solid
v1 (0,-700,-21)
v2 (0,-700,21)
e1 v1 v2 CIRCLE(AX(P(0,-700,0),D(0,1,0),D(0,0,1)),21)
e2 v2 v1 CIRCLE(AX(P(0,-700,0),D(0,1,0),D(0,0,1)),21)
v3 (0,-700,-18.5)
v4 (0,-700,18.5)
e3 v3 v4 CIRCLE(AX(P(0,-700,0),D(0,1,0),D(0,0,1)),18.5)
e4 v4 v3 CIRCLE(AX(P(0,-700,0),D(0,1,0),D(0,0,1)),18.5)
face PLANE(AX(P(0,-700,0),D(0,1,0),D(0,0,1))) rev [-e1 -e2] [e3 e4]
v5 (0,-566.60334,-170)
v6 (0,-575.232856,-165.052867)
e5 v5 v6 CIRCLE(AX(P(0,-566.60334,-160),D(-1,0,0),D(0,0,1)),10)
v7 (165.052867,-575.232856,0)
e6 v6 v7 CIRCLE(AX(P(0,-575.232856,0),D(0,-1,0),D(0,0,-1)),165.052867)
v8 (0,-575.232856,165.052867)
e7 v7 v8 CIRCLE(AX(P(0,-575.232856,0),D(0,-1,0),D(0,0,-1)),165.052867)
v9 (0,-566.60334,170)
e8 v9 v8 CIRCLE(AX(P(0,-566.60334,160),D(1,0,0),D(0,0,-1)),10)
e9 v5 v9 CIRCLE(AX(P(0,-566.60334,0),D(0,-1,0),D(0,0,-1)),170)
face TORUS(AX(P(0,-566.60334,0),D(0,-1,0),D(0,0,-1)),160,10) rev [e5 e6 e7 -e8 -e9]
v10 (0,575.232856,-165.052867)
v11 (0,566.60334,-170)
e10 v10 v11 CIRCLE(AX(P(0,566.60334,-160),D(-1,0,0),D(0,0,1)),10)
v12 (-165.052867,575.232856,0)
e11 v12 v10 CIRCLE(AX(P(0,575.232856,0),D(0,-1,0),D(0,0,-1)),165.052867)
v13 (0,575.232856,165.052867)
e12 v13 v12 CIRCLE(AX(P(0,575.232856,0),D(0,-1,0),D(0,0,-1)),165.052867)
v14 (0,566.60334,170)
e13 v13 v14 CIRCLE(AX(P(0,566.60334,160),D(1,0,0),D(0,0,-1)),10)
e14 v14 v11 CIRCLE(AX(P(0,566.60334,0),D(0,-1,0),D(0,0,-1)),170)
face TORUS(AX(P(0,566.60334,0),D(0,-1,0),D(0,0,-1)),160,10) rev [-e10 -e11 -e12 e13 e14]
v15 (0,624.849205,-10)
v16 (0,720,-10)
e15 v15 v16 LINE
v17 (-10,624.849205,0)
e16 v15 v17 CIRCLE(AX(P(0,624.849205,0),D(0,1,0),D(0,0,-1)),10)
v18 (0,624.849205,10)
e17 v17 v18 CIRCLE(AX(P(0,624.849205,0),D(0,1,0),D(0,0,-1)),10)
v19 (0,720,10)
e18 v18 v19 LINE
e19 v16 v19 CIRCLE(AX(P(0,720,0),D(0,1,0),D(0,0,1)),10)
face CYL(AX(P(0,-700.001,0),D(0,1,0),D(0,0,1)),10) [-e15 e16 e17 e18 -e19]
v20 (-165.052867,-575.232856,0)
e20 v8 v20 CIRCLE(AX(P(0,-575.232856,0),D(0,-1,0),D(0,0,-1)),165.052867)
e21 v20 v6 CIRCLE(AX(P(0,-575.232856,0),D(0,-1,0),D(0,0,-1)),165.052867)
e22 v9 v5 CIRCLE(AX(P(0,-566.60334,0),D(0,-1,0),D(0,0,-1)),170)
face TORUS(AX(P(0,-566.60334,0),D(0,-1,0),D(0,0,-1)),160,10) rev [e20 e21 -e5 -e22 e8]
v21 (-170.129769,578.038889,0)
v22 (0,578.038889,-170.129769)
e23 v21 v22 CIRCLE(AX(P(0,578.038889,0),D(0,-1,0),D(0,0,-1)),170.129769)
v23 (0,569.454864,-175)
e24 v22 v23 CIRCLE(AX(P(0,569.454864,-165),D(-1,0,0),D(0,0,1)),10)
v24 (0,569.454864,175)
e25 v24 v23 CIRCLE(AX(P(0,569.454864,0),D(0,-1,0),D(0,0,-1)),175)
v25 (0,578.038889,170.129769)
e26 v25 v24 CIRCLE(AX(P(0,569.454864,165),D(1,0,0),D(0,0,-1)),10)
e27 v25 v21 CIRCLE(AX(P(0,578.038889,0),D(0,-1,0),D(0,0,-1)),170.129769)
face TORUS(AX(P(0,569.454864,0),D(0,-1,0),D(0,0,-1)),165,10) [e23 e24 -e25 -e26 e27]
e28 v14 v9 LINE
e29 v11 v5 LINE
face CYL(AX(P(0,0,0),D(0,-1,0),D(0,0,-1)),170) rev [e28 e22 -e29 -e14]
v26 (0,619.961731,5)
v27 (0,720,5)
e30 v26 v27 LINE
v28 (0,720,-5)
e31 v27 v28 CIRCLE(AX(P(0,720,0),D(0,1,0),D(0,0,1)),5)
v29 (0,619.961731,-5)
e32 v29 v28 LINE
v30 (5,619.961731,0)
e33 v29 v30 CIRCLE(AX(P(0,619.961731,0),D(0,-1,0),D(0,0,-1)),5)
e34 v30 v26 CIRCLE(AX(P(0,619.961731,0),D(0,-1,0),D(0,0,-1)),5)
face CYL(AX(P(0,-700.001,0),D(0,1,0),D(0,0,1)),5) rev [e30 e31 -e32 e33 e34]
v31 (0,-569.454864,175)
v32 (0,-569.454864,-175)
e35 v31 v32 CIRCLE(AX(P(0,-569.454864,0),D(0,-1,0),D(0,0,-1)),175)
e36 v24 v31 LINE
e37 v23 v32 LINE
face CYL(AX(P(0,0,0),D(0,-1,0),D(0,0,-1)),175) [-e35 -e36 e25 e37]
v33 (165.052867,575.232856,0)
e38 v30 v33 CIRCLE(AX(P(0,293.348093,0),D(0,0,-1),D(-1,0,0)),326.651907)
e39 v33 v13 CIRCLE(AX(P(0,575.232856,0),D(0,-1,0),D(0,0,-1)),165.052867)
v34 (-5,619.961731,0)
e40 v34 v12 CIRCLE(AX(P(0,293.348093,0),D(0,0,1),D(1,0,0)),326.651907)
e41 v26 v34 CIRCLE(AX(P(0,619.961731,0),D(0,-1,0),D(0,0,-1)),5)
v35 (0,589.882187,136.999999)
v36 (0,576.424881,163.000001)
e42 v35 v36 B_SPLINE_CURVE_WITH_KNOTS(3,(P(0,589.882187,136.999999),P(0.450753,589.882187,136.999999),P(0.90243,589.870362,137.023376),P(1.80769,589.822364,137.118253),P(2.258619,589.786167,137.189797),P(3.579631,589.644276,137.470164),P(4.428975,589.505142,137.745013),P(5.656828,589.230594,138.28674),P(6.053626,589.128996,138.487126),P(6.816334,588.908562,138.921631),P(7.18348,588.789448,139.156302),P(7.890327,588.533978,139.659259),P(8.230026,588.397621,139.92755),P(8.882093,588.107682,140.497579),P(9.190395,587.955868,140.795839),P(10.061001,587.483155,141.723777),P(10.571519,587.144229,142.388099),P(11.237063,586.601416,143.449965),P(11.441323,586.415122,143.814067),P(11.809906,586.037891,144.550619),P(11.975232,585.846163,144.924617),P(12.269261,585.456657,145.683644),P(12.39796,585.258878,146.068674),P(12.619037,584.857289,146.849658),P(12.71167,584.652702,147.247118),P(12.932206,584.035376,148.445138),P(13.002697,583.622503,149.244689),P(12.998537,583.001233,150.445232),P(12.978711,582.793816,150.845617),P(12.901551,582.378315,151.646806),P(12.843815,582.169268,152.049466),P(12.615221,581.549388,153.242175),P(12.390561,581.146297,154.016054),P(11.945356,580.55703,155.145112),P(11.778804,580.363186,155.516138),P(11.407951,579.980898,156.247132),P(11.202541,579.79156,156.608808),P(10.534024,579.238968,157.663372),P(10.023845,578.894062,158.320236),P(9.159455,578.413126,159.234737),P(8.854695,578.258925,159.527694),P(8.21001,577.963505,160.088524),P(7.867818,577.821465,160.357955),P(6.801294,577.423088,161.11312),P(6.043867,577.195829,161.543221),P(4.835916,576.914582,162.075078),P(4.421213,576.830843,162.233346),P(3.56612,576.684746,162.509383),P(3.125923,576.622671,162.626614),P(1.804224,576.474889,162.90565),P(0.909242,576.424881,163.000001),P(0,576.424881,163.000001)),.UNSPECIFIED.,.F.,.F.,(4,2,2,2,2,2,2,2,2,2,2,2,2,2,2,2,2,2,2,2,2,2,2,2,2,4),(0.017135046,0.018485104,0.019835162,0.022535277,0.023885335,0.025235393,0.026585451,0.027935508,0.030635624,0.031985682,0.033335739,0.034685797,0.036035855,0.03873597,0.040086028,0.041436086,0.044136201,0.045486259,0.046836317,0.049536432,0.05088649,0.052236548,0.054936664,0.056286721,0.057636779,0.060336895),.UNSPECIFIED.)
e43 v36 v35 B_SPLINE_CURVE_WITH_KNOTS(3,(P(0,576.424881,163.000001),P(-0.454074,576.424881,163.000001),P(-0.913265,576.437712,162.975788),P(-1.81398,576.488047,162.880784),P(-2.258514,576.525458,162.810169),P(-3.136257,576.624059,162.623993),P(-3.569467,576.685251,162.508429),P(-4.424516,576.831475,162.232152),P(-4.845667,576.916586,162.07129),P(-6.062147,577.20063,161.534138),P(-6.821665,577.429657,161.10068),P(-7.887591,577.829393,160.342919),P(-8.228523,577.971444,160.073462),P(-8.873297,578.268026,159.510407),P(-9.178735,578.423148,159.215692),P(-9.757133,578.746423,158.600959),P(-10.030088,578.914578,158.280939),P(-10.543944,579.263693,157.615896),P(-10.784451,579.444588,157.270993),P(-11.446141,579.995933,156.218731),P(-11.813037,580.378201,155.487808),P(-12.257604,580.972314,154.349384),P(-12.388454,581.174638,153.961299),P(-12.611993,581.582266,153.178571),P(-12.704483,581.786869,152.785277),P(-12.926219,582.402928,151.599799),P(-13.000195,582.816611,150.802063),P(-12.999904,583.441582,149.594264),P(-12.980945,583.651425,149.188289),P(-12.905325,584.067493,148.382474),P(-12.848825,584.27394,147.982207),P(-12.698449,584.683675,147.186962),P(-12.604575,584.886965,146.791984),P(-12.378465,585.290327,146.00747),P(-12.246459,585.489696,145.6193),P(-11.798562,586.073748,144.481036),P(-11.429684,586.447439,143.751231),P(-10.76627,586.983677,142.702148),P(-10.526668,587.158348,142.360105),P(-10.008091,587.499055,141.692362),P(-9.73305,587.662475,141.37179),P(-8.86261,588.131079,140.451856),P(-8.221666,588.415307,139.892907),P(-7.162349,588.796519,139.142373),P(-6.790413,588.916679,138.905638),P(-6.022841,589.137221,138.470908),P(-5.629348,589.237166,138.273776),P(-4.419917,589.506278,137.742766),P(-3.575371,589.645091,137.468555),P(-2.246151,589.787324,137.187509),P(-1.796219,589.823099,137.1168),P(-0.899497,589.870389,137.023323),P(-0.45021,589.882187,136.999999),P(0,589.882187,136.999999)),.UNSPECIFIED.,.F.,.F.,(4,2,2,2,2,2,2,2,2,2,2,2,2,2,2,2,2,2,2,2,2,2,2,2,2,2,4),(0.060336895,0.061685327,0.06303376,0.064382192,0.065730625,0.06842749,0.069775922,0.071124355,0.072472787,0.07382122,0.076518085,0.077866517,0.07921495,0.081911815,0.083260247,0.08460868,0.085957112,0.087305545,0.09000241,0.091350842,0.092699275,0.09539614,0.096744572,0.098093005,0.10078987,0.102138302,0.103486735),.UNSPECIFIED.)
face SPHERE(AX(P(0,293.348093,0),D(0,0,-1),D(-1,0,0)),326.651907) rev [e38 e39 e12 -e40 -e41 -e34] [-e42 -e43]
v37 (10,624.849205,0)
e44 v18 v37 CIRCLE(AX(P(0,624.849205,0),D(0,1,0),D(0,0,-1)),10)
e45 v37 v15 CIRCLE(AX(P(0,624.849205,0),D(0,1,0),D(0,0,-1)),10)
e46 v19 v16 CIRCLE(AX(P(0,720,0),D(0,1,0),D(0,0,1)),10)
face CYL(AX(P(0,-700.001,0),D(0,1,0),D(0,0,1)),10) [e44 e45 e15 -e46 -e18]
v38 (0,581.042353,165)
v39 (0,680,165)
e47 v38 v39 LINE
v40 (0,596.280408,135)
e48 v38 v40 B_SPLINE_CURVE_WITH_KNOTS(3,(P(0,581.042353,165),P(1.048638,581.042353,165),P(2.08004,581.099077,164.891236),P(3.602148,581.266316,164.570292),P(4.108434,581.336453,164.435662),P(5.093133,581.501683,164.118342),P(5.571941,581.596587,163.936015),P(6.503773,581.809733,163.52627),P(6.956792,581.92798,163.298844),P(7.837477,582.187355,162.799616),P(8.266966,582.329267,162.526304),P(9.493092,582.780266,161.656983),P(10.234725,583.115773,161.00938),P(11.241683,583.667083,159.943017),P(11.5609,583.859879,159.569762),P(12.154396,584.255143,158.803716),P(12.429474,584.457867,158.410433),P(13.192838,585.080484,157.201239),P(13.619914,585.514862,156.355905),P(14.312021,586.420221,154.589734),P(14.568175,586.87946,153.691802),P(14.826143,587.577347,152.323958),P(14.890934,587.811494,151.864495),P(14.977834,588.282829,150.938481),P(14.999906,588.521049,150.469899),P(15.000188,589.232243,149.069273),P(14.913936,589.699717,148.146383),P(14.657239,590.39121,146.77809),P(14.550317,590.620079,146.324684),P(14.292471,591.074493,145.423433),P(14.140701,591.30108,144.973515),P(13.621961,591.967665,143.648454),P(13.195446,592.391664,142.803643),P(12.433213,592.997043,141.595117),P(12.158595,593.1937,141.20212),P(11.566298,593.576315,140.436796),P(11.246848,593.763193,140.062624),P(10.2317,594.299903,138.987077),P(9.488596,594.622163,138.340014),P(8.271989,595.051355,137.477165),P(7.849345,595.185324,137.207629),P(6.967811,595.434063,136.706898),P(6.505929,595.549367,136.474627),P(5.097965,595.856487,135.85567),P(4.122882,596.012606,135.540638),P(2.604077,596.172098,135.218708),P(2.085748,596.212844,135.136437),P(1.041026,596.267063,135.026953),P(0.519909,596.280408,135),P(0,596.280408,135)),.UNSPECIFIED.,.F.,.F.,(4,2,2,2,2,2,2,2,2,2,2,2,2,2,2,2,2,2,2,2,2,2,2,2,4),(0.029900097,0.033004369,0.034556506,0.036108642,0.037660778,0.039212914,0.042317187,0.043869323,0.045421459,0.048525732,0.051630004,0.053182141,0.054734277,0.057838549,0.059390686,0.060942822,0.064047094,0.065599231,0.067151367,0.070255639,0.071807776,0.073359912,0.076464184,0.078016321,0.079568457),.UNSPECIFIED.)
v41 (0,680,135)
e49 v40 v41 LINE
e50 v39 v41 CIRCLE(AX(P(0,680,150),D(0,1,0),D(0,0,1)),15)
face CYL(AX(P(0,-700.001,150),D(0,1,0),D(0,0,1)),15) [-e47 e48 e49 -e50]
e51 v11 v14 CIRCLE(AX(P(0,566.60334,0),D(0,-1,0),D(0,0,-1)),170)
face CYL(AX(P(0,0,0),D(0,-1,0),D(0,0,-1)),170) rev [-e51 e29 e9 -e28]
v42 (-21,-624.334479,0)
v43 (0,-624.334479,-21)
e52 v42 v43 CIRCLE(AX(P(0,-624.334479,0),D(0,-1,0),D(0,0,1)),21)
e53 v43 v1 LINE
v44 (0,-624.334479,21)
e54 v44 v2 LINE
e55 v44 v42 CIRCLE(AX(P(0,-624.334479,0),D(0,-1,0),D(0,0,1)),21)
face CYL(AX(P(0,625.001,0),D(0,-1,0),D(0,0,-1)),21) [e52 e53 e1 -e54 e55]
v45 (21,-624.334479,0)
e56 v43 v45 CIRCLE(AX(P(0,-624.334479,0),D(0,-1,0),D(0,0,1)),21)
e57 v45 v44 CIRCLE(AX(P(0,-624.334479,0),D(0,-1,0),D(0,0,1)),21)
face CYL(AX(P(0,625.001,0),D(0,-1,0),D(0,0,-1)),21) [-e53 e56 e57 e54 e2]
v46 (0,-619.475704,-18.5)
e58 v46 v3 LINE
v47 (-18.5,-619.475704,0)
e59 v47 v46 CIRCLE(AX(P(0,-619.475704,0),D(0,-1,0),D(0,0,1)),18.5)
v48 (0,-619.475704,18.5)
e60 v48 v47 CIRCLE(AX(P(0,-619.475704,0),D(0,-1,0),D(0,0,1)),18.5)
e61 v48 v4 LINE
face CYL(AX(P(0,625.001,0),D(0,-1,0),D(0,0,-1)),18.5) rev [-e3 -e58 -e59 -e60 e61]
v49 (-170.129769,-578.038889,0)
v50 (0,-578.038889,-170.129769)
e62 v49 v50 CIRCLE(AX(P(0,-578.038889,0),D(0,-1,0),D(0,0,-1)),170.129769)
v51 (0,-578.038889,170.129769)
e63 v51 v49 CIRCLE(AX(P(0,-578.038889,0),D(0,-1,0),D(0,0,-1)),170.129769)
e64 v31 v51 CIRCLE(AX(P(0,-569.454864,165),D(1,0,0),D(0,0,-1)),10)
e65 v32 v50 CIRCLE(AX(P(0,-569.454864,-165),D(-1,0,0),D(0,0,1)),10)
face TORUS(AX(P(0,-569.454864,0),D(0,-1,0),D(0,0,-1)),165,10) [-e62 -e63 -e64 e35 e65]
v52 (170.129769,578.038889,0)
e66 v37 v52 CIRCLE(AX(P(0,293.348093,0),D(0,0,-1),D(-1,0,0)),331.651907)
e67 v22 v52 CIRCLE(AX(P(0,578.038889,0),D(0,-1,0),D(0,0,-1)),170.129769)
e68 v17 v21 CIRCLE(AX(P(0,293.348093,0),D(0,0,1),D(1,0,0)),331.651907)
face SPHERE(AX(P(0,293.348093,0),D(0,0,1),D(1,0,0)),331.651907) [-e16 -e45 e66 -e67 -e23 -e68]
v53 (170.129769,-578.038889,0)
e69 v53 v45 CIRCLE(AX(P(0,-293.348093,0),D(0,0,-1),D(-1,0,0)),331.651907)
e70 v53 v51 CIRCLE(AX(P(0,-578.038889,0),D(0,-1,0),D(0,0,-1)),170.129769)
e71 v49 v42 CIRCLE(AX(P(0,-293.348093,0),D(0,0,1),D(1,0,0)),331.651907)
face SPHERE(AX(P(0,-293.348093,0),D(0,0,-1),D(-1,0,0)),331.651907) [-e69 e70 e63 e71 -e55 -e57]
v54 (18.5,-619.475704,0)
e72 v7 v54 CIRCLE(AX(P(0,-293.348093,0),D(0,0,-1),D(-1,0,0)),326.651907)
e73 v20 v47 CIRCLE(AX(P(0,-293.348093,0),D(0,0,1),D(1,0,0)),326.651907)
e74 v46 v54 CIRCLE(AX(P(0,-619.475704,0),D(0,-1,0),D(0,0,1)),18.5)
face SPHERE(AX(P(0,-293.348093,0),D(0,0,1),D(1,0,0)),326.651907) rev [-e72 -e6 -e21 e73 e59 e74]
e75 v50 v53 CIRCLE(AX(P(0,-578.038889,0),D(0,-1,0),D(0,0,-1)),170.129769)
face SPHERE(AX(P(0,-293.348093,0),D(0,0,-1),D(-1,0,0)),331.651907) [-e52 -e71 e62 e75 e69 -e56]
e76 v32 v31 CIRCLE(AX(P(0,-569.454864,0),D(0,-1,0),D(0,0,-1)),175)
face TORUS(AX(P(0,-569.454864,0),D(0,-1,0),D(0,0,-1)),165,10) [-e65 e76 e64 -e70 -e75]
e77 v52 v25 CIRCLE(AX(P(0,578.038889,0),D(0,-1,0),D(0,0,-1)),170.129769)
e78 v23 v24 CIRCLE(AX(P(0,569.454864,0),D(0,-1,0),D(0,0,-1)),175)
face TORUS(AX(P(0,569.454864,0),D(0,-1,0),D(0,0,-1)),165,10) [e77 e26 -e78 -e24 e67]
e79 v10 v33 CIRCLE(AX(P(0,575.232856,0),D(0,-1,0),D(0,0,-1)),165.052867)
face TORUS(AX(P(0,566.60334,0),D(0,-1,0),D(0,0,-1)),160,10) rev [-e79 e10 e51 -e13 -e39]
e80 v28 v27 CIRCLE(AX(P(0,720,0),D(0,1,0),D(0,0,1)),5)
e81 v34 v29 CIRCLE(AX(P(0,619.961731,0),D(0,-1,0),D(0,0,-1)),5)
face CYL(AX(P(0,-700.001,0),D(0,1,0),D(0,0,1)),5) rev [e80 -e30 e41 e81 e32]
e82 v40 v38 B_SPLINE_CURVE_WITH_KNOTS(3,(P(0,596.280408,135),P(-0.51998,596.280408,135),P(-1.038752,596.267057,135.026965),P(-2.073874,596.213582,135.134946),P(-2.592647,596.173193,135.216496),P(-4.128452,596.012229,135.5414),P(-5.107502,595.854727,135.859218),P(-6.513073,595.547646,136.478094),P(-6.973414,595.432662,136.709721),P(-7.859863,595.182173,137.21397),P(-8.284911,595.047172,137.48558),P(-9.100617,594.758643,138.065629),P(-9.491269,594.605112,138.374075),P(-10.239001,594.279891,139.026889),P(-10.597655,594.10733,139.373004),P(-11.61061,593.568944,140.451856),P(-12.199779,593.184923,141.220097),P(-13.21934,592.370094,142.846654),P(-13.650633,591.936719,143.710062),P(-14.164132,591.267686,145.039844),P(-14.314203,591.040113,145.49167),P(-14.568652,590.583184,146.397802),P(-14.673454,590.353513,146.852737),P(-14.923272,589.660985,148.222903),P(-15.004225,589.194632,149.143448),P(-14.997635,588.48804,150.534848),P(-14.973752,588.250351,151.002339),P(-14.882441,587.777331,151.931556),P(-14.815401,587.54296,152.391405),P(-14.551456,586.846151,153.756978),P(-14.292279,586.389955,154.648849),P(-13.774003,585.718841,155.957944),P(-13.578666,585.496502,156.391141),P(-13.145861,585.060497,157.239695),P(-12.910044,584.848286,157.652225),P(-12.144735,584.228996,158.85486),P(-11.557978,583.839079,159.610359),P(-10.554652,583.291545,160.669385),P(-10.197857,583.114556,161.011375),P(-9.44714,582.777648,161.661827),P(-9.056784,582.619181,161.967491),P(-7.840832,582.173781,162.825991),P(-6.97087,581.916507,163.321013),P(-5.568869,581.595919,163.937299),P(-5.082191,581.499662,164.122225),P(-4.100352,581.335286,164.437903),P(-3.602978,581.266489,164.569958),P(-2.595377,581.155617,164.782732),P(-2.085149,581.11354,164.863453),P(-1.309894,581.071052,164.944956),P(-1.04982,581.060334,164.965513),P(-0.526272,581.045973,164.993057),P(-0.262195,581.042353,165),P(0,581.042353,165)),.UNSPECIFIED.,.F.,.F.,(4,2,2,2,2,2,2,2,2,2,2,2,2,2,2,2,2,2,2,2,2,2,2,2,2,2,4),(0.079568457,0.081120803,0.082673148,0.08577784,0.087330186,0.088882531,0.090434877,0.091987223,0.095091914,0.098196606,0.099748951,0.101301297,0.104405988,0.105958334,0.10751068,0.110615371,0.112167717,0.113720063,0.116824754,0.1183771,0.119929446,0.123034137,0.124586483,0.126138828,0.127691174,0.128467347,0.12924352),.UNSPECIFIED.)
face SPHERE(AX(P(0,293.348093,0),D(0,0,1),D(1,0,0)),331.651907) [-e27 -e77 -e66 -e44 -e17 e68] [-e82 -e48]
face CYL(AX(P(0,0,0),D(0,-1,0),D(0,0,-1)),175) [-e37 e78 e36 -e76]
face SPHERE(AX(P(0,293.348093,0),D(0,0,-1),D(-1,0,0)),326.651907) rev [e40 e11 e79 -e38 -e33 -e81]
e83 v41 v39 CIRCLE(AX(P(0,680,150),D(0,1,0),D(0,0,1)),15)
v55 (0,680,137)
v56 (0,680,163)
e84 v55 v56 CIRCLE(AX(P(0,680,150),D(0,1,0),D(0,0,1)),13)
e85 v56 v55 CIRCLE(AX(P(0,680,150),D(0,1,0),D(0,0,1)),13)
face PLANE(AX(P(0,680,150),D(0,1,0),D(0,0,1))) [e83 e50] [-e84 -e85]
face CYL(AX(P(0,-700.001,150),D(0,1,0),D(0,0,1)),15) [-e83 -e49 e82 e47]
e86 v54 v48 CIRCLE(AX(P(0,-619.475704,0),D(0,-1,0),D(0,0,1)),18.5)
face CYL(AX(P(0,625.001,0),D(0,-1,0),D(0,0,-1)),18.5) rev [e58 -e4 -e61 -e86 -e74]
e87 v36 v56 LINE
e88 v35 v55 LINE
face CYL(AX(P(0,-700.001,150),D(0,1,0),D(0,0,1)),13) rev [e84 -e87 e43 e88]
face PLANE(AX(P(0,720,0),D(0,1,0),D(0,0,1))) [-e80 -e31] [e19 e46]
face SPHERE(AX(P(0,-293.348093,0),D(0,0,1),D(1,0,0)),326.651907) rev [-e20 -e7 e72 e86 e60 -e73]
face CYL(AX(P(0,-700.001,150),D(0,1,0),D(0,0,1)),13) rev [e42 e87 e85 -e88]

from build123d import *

# Parameters (mm, degrees)
BOSS_EXTRUDE1_REACH      = 1349.915
BOSS_EXTRUDE1_END_RADIUS = 331.651906797
SKETCH2_R                = 21
SKETCH2_R_2              = 18.5
SKETCH3_R                = 18.5
CUT_EXTRUDE1_DEPTH       = 526
BOSS_EXTRUDE3_REACH      = 1443.406
BOSS_EXTRUDE3_END_RADIUS = 331.651906797
SKETCH5_R                = 10
SKETCH5_R_2              = 5
SKETCH6_R                = 5
CUT_EXTRUDE2_DEPTH       = 190
BOSS_EXTRUDE5_REACH      = 1404.016
BOSS_EXTRUDE5_END_RADIUS = 331.651906797
SKETCH8_R                = 15
SKETCH8_R_2              = 13
SKETCH9_R                = 13.000001432
CUT_EXTRUDE3_DEPTH       = 107


with BuildPart() as part:
    # Sketch1 → Revolve1 (revolve)
    with BuildSketch(Plane.XY, mode=Mode.PRIVATE) as revolve1_sk:
        with BuildLine():
            Line((175, -569.454864482), (175, 569.454864482))
            ThreePointArc((175, 569.454864482), (173.697634466, 574.389553398), (170.129769061, 578.03888856))
            ThreePointArc((170.129769061, 578.03888856), (88.246082503, 613.044224248), (0, 625))
            Line((0, 625), (0, 620))
            ThreePointArc((0, 620), (85.508108026, 608.609622217), (165.052867094, 575.232855612))
            ThreePointArc((165.052867094, 575.232855612), (168.67550203, 571.57683653), (170, 566.603340322))
            Line((170, 566.603340322), (170, -566.603340322))
            ThreePointArc((170, -566.603340322), (168.67550203, -571.57683653), (165.052867094, -575.232855612))
            ThreePointArc((165.052867094, -575.232855612), (85.508108026, -608.609622217), (0, -620))
            Line((0, -620), (0, -625))
            ThreePointArc((0, -625), (88.246082503, -613.044224248), (170.129769061, -578.03888856))
            ThreePointArc((170.129769061, -578.03888856), (173.697634466, -574.389553398), (175, -569.454864482))
        make_face()
    revolve(revolve1_sk.sketch.rotate(Axis((0, 0, 0), (0, 1, 0)), 90), axis=Axis((0, 0, 0), (0, 1, 0)))

    # Boss-Extrude1: up to this sphere (the profile starts outside it)
    boss_extrude1_end = Location((0, -293.348093203, 0)) * Sphere(BOSS_EXTRUDE1_END_RADIUS, mode=Mode.PRIVATE)
    # Sketch2 → Boss-Extrude1 (add, up to the surface)
    with BuildSketch(Plane(origin=(0, -700, 0), x_dir=(1, 0, 0), z_dir=(0, 1, 0)), mode=Mode.PRIVATE) as boss_extrude1_sk1:
        with Locations(Location((0, 0, 0), (0, 0, 180))):
            Circle(SKETCH2_R)
        with Locations(Location((0, 0, 0), (0, 0, 270))):
            Circle(SKETCH2_R_2, mode=Mode.SUBTRACT)
    boss_extrude1_tool1 = extrude(boss_extrude1_sk1.sketch, amount=BOSS_EXTRUDE1_REACH, mode=Mode.PRIVATE) - boss_extrude1_end
    add(boss_extrude1_tool1.solids().sort_by_distance((20.40603, -700, 0))[0])

    # Sketch3 → Cut-Extrude1 (cut)
    with BuildSketch(Plane(origin=(0, -700, 0), x_dir=(1, 0, 0), z_dir=(0, 1, 0))):
        Circle(SKETCH3_R)
    extrude(amount=CUT_EXTRUDE1_DEPTH, mode=Mode.SUBTRACT)

    # Boss-Extrude3: up to this sphere (the profile starts outside it)
    boss_extrude3_end = Location((0, 293.348093203, 0)) * Sphere(BOSS_EXTRUDE3_END_RADIUS, mode=Mode.PRIVATE)
    # Sketch5 → Boss-Extrude3 (add, up to the surface)
    with BuildSketch(Plane(origin=(0, 720, 0), x_dir=(1, 0, 0), z_dir=(0, 1, 0)), mode=Mode.PRIVATE) as boss_extrude3_sk1:
        with Locations(Location((0, 0, 0), (0, 0, 270))):
            Circle(SKETCH5_R)
        with Locations(Location((0, 0, 0), (0, 0, 270))):
            Circle(SKETCH5_R_2, mode=Mode.SUBTRACT)
    boss_extrude3_tool1 = extrude(boss_extrude3_sk1.sketch, amount=-BOSS_EXTRUDE3_REACH, mode=Mode.PRIVATE) - boss_extrude3_end
    add(boss_extrude3_tool1.solids().sort_by_distance((0, 720, -9.717157))[0])

    # Sketch6 → Cut-Extrude2 (cut)
    with BuildSketch(Plane(origin=(0, 720, 0), x_dir=(1, 0, 0), z_dir=(0, 1, 0))):
        with Locations(Location((0, 0, 0), (0, 0, 270))):
            Circle(SKETCH6_R)
    extrude(amount=-CUT_EXTRUDE2_DEPTH, mode=Mode.SUBTRACT)

    # Boss-Extrude5: up to this sphere (the profile starts outside it)
    boss_extrude5_end = Location((0, 293.348093203, 0)) * Sphere(BOSS_EXTRUDE5_END_RADIUS, mode=Mode.PRIVATE)
    # Sketch8 → Boss-Extrude5 (add, up to the surface)
    with BuildSketch(Plane(origin=(0, 680, 0), x_dir=(1, 0, 0), z_dir=(0, 1, 0)), mode=Mode.PRIVATE) as boss_extrude5_sk1:
        with Locations(Location((0, -150, 0), (0, 0, 270.000000007))):
            Circle(SKETCH8_R)
        with Locations(Location((0, -150, 0), (0, 0, 270))):
            Circle(SKETCH8_R_2, mode=Mode.SUBTRACT)
    boss_extrude5_tool1 = extrude(boss_extrude5_sk1.sketch, amount=-BOSS_EXTRUDE5_REACH, mode=Mode.PRIVATE) - boss_extrude5_end
    add(boss_extrude5_tool1.solids().sort_by_distance((0, 680, 135.424264))[0])

    # Sketch9 → Cut-Extrude3 (cut)
    with BuildSketch(Plane(origin=(0, 680, 0), x_dir=(1, 0, 0), z_dir=(0, 1, 0))):
        with Locations(Location((0, -150, 0), (0, 0, 270))):
            Circle(SKETCH9_R)
    extrude(amount=-CUT_EXTRUDE3_DEPTH, mode=Mode.SUBTRACT)


solid = part.part
